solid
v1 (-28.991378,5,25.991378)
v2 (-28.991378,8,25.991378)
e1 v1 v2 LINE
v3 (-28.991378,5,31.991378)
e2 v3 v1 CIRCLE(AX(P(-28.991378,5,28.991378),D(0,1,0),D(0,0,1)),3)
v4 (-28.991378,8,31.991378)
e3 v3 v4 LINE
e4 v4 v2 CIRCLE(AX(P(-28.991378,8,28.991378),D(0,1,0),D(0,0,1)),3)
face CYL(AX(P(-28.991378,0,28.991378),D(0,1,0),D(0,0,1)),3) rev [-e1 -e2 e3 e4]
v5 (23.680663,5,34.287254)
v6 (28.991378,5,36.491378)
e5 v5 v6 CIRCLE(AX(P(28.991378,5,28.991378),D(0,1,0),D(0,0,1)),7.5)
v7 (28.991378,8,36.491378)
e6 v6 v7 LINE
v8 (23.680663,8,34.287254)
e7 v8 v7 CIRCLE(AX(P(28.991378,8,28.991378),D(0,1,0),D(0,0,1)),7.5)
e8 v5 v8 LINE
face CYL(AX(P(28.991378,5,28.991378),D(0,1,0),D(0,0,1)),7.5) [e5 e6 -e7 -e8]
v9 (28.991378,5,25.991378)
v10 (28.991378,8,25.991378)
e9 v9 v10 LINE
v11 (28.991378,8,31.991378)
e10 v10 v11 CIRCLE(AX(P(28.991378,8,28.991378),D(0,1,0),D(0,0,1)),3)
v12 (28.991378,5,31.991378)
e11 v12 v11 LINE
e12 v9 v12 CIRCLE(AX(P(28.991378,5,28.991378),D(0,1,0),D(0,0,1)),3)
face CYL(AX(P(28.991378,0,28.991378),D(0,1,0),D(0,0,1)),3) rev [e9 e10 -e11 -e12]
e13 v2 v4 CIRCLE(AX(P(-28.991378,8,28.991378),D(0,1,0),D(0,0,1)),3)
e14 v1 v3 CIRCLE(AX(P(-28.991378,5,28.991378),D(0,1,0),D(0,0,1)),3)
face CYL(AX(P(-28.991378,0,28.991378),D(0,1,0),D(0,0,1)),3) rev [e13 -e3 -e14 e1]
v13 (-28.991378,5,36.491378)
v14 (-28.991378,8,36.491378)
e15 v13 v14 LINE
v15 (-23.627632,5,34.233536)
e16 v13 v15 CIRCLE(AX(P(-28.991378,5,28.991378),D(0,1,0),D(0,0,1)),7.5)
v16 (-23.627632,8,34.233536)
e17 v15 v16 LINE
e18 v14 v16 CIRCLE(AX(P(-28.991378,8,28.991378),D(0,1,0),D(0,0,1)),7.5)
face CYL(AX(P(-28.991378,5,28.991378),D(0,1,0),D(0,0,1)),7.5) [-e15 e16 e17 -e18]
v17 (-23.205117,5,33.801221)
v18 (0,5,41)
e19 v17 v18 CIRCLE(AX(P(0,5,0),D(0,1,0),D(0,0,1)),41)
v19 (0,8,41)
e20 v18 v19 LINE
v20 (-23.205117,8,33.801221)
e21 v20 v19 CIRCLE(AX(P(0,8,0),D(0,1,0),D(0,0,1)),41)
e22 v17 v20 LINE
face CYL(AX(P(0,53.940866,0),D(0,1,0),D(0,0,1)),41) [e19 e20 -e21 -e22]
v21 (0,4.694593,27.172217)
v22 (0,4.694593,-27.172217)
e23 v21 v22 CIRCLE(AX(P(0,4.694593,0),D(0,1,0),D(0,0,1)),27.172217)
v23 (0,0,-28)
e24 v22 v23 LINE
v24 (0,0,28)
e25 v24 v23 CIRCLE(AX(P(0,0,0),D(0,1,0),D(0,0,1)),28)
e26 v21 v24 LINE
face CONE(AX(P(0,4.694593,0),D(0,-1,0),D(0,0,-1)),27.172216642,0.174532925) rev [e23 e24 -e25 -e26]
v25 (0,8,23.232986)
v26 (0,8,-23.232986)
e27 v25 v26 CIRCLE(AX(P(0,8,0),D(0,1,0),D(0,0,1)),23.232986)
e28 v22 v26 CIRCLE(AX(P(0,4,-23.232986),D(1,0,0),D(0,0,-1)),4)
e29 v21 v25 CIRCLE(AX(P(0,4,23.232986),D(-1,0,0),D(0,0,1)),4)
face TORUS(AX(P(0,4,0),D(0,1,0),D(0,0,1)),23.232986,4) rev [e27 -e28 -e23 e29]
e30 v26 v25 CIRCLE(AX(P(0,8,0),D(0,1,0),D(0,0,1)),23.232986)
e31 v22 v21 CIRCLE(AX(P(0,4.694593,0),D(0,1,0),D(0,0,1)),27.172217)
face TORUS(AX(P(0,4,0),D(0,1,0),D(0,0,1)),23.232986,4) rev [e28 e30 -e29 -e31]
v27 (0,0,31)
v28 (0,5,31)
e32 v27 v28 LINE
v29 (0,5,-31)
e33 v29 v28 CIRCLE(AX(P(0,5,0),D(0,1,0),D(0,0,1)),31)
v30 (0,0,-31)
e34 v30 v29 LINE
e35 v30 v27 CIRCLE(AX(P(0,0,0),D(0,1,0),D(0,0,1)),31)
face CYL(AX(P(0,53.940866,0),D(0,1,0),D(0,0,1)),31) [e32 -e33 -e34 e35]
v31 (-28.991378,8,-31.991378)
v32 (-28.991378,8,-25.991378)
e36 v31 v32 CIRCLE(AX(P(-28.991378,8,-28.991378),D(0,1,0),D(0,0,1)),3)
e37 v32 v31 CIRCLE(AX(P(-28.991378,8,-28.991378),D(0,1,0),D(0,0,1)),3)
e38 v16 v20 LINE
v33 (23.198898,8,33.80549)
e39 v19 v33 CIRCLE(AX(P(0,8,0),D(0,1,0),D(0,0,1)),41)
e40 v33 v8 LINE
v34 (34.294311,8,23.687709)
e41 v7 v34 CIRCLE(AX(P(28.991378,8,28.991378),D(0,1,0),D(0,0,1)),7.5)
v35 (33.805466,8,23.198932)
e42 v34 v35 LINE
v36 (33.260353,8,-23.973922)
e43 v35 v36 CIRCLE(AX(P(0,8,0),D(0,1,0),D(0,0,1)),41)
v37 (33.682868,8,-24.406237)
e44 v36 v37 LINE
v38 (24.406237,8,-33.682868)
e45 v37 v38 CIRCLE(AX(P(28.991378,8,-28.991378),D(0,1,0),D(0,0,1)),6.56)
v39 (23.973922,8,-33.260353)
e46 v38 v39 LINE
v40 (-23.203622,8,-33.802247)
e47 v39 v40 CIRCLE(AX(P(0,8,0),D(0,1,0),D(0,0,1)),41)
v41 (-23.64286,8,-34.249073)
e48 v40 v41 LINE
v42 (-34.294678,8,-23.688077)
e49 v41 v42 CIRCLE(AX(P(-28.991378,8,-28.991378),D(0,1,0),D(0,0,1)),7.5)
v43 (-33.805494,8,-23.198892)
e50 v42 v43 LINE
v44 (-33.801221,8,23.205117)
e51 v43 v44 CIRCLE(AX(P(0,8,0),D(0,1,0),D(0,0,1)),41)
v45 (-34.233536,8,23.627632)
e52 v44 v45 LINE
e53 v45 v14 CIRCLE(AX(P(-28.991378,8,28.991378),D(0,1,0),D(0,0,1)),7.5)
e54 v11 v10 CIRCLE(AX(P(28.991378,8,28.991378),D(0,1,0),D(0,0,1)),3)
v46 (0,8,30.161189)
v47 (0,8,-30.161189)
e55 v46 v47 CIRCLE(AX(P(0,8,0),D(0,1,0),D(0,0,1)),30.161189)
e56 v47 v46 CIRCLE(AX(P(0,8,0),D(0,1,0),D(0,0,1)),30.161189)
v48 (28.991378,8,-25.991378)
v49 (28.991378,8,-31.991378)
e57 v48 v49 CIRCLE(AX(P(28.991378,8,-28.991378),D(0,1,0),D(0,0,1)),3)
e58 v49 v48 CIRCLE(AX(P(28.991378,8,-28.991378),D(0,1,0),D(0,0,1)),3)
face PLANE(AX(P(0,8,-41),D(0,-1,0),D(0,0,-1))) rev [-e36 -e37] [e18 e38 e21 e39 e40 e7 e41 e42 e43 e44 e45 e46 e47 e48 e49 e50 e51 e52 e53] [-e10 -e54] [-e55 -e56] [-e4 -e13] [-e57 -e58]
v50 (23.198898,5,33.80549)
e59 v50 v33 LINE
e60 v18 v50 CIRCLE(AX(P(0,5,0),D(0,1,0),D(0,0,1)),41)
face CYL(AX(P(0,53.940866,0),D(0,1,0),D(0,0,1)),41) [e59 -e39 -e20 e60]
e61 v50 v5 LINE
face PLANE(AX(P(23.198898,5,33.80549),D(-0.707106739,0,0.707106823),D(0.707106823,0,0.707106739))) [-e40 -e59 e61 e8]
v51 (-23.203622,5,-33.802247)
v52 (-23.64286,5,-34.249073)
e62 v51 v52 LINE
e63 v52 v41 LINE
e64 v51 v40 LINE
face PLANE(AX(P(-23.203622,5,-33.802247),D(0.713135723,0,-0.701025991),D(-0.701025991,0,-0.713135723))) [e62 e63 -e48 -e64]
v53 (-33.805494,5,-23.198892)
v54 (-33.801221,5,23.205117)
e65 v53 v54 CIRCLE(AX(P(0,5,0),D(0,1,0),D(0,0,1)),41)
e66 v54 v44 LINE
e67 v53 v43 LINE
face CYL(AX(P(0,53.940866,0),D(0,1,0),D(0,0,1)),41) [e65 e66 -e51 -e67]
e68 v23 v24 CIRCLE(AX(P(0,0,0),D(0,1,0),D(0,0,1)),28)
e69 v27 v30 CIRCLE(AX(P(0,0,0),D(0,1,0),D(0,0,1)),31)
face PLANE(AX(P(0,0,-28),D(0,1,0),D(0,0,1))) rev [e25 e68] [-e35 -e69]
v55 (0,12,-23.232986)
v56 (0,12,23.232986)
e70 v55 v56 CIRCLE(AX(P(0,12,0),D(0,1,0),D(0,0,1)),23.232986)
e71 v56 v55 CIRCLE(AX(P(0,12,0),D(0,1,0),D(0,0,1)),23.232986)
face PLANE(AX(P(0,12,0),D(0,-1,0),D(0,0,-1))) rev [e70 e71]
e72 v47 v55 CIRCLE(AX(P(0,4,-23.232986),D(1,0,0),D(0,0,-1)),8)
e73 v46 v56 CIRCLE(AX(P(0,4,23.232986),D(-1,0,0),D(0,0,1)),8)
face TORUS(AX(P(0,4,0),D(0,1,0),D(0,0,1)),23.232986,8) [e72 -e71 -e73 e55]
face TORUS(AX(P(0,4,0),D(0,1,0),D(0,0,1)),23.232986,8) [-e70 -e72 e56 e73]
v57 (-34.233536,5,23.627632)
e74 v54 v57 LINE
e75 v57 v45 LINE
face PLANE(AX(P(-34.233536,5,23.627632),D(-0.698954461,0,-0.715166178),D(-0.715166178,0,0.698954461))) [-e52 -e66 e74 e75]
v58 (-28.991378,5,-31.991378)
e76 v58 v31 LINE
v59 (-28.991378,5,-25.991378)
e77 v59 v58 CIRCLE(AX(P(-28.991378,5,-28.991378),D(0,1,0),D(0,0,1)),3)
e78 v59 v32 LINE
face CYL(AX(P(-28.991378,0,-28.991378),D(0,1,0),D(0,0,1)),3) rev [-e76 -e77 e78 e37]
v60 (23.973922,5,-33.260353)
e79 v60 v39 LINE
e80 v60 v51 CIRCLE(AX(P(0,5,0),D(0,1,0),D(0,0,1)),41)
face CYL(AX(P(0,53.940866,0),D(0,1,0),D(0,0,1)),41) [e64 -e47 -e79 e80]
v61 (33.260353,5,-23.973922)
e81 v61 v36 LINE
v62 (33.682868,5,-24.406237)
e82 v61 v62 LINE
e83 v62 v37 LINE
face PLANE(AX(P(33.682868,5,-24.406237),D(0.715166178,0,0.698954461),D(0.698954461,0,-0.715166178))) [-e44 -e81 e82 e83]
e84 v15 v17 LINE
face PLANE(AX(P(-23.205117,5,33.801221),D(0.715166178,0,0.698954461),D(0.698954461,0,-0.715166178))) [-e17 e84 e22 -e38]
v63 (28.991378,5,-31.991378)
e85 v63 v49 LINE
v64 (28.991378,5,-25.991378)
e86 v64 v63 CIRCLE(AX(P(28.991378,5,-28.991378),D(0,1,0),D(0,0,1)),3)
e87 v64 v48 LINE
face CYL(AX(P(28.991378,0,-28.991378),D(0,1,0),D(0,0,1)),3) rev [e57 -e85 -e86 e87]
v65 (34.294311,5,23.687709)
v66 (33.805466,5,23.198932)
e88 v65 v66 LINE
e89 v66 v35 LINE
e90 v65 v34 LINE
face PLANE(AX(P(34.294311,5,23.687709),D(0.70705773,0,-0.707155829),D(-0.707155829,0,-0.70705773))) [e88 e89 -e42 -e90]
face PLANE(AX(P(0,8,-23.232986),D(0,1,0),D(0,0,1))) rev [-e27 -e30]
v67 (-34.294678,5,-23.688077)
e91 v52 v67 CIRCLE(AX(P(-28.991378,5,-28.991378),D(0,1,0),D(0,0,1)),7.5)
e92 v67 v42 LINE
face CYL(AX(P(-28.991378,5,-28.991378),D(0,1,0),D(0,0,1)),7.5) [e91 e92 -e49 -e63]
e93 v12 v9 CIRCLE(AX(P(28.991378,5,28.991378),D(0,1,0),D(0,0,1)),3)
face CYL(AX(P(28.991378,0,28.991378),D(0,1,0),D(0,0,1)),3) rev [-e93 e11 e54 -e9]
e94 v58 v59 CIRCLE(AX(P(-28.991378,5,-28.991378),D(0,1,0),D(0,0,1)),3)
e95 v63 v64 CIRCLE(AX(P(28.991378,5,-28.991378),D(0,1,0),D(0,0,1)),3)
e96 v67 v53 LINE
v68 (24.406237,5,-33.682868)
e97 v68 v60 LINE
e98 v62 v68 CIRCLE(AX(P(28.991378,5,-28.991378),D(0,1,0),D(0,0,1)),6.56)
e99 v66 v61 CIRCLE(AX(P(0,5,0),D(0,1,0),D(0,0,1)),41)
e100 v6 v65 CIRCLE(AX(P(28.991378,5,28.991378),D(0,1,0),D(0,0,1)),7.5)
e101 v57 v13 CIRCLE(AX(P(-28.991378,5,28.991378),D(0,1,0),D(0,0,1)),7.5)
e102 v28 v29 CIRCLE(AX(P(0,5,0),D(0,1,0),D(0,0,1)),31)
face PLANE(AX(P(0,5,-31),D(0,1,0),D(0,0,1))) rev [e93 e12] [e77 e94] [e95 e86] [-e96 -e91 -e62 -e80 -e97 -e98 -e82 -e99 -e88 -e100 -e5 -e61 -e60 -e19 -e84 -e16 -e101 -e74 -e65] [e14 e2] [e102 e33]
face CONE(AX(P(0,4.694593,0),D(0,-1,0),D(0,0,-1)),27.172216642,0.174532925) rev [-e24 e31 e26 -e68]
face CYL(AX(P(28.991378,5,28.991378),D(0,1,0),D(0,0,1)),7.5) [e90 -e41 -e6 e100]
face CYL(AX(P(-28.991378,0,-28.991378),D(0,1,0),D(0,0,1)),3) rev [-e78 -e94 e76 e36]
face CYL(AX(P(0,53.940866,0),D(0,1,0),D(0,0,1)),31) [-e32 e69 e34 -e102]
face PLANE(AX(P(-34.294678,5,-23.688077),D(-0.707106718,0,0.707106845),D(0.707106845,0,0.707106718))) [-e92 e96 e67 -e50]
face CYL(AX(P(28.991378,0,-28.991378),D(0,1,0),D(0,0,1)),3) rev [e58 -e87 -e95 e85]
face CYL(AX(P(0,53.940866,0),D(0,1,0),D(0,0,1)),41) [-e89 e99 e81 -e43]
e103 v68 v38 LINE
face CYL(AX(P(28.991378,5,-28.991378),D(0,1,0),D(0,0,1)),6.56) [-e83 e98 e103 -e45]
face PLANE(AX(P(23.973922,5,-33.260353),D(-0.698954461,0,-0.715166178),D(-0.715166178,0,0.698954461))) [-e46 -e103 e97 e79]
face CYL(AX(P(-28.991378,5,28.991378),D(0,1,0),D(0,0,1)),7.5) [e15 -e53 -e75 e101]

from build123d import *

# Parameters (mm, degrees)
EXTRUDE_START       = -3
SKETCH_2_R          = 35.459459581
EXTRUDE_1_DEPTH     = 3
SKETCH_4_R          = 3
CUT_EXTRUDE_1_DEPTH = 59.532042507


with BuildPart() as part:
    # 草图1 → 旋转1 (revolve)
    with BuildSketch(Plane(origin=(0, 0, 0), x_dir=(0, 0, -1), z_dir=(1, 0, 0)), mode=Mode.PRIVATE) as revolve_1_sk:
        with BuildLine():
            Line((0, 12), (23.23298563, 12))
            ThreePointArc((23.23298563, 12), (27.23298563, 10.92820323), (30.16118886, 8))
            Line((30.16118886, 8), (41, 8))
            Line((41, 8), (41, 5))
            Line((41, 5), (31, 5))
            Line((31, 5), (31, 0))
            Line((31, 0), (28, 0))
            Line((28, 0), (27.172216642, 4.694592711))
            ThreePointArc((27.172216642, 4.694592711), (25.804136068, 7.064177772), (23.23298563, 8))
            Line((23.23298563, 8), (21.200995797, 8))
            Line((21.200995797, 8), (0, 8))
            Line((0, 8), (0, 12))
        make_face()
    revolve(revolve_1_sk.sketch.rotate(Axis((0, 53.940866142, 0), (0, -1, 0)), 180), axis=Axis((0, 53.940866142, 0), (0, -1, 0)))

    # 草图2 → 凸台-拉伸1 (add)
    with BuildSketch(Plane(origin=(0, 8, 0), x_dir=(1, 0, 0), z_dir=(0, 1, 0)).offset(EXTRUDE_START)):
        with BuildLine():
            Line((-34.294678434, 23.688076669), (-33.80549374, 23.198892063))
            ThreePointArc((-33.80549374, 23.198892063), (-40.999999826, -0.003774812), (-33.801221389, -23.205116518))
            Line((-33.801221389, -23.205116518), (-34.233536486, -23.627631697))
            ThreePointArc((-34.233536486, -23.627631697), (-34.294678888, -34.294678888), (-23.627631697, -34.233536486))
            Line((-23.627631697, -34.233536486), (-23.205116518, -33.801221389))
            ThreePointArc((-23.205116518, -33.801221389), (-0.003771108, -40.999999827), (23.198898172, -33.805489549))
            Line((23.198898172, -33.805489549), (23.680662822, -34.287254142))
            ThreePointArc((23.680662822, -34.287254142), (34.291151869, -34.298203544), (34.294310993, -23.687709319))
            Line((34.294310993, -23.687709319), (33.805466141, -23.198932281))
            ThreePointArc((33.805466141, -23.198932281), (40.997262845, 0.473750181), (33.260352966, 23.973921676))
            Line((33.260352966, 23.973921676), (33.682868145, 24.406236773))
            ThreePointArc((33.682868145, 24.406236773), (33.629998505, 33.629998505), (24.406236773, 33.682868145))
            Line((24.406236773, 33.682868145), (23.973921676, 33.260352966))
            ThreePointArc((23.973921676, 33.260352966), (0.470906346, 40.997295609), (-23.203621987, 33.802247362))
            Line((-23.203621987, 33.802247362), (-23.642860481, 34.249073393))
            ThreePointArc((-23.642860481, 34.249073393), (-34.27192479, 34.317335821), (-34.294678434, 23.688076669))
        make_face()
        Circle(SKETCH_2_R, mode=Mode.SUBTRACT)
    extrude(amount=EXTRUDE_1_DEPTH)

    # 草图4 → 切除-拉伸1 (cut, through all)
    with BuildSketch(Plane(origin=(0, 8, 0), x_dir=(1, 0, 0), z_dir=(0, 1, 0))):
        with Locations(Location((-28.991378029, 28.991378029, 0), (0, 0, 270))):
            Circle(SKETCH_4_R)
        with Locations(Location((28.991378029, 28.991378029, 0), (0, 0, 270))):
            Circle(SKETCH_4_R)
        with Locations(Location((28.991378029, -28.991378029, 0), (0, 0, 270))):
            Circle(SKETCH_4_R)
        with Locations(Location((-28.991378029, -28.991378029, 0), (0, 0, 270))):
            Circle(SKETCH_4_R)
    extrude(amount=-CUT_EXTRUDE_1_DEPTH, mode=Mode.SUBTRACT)


solid = part.part
